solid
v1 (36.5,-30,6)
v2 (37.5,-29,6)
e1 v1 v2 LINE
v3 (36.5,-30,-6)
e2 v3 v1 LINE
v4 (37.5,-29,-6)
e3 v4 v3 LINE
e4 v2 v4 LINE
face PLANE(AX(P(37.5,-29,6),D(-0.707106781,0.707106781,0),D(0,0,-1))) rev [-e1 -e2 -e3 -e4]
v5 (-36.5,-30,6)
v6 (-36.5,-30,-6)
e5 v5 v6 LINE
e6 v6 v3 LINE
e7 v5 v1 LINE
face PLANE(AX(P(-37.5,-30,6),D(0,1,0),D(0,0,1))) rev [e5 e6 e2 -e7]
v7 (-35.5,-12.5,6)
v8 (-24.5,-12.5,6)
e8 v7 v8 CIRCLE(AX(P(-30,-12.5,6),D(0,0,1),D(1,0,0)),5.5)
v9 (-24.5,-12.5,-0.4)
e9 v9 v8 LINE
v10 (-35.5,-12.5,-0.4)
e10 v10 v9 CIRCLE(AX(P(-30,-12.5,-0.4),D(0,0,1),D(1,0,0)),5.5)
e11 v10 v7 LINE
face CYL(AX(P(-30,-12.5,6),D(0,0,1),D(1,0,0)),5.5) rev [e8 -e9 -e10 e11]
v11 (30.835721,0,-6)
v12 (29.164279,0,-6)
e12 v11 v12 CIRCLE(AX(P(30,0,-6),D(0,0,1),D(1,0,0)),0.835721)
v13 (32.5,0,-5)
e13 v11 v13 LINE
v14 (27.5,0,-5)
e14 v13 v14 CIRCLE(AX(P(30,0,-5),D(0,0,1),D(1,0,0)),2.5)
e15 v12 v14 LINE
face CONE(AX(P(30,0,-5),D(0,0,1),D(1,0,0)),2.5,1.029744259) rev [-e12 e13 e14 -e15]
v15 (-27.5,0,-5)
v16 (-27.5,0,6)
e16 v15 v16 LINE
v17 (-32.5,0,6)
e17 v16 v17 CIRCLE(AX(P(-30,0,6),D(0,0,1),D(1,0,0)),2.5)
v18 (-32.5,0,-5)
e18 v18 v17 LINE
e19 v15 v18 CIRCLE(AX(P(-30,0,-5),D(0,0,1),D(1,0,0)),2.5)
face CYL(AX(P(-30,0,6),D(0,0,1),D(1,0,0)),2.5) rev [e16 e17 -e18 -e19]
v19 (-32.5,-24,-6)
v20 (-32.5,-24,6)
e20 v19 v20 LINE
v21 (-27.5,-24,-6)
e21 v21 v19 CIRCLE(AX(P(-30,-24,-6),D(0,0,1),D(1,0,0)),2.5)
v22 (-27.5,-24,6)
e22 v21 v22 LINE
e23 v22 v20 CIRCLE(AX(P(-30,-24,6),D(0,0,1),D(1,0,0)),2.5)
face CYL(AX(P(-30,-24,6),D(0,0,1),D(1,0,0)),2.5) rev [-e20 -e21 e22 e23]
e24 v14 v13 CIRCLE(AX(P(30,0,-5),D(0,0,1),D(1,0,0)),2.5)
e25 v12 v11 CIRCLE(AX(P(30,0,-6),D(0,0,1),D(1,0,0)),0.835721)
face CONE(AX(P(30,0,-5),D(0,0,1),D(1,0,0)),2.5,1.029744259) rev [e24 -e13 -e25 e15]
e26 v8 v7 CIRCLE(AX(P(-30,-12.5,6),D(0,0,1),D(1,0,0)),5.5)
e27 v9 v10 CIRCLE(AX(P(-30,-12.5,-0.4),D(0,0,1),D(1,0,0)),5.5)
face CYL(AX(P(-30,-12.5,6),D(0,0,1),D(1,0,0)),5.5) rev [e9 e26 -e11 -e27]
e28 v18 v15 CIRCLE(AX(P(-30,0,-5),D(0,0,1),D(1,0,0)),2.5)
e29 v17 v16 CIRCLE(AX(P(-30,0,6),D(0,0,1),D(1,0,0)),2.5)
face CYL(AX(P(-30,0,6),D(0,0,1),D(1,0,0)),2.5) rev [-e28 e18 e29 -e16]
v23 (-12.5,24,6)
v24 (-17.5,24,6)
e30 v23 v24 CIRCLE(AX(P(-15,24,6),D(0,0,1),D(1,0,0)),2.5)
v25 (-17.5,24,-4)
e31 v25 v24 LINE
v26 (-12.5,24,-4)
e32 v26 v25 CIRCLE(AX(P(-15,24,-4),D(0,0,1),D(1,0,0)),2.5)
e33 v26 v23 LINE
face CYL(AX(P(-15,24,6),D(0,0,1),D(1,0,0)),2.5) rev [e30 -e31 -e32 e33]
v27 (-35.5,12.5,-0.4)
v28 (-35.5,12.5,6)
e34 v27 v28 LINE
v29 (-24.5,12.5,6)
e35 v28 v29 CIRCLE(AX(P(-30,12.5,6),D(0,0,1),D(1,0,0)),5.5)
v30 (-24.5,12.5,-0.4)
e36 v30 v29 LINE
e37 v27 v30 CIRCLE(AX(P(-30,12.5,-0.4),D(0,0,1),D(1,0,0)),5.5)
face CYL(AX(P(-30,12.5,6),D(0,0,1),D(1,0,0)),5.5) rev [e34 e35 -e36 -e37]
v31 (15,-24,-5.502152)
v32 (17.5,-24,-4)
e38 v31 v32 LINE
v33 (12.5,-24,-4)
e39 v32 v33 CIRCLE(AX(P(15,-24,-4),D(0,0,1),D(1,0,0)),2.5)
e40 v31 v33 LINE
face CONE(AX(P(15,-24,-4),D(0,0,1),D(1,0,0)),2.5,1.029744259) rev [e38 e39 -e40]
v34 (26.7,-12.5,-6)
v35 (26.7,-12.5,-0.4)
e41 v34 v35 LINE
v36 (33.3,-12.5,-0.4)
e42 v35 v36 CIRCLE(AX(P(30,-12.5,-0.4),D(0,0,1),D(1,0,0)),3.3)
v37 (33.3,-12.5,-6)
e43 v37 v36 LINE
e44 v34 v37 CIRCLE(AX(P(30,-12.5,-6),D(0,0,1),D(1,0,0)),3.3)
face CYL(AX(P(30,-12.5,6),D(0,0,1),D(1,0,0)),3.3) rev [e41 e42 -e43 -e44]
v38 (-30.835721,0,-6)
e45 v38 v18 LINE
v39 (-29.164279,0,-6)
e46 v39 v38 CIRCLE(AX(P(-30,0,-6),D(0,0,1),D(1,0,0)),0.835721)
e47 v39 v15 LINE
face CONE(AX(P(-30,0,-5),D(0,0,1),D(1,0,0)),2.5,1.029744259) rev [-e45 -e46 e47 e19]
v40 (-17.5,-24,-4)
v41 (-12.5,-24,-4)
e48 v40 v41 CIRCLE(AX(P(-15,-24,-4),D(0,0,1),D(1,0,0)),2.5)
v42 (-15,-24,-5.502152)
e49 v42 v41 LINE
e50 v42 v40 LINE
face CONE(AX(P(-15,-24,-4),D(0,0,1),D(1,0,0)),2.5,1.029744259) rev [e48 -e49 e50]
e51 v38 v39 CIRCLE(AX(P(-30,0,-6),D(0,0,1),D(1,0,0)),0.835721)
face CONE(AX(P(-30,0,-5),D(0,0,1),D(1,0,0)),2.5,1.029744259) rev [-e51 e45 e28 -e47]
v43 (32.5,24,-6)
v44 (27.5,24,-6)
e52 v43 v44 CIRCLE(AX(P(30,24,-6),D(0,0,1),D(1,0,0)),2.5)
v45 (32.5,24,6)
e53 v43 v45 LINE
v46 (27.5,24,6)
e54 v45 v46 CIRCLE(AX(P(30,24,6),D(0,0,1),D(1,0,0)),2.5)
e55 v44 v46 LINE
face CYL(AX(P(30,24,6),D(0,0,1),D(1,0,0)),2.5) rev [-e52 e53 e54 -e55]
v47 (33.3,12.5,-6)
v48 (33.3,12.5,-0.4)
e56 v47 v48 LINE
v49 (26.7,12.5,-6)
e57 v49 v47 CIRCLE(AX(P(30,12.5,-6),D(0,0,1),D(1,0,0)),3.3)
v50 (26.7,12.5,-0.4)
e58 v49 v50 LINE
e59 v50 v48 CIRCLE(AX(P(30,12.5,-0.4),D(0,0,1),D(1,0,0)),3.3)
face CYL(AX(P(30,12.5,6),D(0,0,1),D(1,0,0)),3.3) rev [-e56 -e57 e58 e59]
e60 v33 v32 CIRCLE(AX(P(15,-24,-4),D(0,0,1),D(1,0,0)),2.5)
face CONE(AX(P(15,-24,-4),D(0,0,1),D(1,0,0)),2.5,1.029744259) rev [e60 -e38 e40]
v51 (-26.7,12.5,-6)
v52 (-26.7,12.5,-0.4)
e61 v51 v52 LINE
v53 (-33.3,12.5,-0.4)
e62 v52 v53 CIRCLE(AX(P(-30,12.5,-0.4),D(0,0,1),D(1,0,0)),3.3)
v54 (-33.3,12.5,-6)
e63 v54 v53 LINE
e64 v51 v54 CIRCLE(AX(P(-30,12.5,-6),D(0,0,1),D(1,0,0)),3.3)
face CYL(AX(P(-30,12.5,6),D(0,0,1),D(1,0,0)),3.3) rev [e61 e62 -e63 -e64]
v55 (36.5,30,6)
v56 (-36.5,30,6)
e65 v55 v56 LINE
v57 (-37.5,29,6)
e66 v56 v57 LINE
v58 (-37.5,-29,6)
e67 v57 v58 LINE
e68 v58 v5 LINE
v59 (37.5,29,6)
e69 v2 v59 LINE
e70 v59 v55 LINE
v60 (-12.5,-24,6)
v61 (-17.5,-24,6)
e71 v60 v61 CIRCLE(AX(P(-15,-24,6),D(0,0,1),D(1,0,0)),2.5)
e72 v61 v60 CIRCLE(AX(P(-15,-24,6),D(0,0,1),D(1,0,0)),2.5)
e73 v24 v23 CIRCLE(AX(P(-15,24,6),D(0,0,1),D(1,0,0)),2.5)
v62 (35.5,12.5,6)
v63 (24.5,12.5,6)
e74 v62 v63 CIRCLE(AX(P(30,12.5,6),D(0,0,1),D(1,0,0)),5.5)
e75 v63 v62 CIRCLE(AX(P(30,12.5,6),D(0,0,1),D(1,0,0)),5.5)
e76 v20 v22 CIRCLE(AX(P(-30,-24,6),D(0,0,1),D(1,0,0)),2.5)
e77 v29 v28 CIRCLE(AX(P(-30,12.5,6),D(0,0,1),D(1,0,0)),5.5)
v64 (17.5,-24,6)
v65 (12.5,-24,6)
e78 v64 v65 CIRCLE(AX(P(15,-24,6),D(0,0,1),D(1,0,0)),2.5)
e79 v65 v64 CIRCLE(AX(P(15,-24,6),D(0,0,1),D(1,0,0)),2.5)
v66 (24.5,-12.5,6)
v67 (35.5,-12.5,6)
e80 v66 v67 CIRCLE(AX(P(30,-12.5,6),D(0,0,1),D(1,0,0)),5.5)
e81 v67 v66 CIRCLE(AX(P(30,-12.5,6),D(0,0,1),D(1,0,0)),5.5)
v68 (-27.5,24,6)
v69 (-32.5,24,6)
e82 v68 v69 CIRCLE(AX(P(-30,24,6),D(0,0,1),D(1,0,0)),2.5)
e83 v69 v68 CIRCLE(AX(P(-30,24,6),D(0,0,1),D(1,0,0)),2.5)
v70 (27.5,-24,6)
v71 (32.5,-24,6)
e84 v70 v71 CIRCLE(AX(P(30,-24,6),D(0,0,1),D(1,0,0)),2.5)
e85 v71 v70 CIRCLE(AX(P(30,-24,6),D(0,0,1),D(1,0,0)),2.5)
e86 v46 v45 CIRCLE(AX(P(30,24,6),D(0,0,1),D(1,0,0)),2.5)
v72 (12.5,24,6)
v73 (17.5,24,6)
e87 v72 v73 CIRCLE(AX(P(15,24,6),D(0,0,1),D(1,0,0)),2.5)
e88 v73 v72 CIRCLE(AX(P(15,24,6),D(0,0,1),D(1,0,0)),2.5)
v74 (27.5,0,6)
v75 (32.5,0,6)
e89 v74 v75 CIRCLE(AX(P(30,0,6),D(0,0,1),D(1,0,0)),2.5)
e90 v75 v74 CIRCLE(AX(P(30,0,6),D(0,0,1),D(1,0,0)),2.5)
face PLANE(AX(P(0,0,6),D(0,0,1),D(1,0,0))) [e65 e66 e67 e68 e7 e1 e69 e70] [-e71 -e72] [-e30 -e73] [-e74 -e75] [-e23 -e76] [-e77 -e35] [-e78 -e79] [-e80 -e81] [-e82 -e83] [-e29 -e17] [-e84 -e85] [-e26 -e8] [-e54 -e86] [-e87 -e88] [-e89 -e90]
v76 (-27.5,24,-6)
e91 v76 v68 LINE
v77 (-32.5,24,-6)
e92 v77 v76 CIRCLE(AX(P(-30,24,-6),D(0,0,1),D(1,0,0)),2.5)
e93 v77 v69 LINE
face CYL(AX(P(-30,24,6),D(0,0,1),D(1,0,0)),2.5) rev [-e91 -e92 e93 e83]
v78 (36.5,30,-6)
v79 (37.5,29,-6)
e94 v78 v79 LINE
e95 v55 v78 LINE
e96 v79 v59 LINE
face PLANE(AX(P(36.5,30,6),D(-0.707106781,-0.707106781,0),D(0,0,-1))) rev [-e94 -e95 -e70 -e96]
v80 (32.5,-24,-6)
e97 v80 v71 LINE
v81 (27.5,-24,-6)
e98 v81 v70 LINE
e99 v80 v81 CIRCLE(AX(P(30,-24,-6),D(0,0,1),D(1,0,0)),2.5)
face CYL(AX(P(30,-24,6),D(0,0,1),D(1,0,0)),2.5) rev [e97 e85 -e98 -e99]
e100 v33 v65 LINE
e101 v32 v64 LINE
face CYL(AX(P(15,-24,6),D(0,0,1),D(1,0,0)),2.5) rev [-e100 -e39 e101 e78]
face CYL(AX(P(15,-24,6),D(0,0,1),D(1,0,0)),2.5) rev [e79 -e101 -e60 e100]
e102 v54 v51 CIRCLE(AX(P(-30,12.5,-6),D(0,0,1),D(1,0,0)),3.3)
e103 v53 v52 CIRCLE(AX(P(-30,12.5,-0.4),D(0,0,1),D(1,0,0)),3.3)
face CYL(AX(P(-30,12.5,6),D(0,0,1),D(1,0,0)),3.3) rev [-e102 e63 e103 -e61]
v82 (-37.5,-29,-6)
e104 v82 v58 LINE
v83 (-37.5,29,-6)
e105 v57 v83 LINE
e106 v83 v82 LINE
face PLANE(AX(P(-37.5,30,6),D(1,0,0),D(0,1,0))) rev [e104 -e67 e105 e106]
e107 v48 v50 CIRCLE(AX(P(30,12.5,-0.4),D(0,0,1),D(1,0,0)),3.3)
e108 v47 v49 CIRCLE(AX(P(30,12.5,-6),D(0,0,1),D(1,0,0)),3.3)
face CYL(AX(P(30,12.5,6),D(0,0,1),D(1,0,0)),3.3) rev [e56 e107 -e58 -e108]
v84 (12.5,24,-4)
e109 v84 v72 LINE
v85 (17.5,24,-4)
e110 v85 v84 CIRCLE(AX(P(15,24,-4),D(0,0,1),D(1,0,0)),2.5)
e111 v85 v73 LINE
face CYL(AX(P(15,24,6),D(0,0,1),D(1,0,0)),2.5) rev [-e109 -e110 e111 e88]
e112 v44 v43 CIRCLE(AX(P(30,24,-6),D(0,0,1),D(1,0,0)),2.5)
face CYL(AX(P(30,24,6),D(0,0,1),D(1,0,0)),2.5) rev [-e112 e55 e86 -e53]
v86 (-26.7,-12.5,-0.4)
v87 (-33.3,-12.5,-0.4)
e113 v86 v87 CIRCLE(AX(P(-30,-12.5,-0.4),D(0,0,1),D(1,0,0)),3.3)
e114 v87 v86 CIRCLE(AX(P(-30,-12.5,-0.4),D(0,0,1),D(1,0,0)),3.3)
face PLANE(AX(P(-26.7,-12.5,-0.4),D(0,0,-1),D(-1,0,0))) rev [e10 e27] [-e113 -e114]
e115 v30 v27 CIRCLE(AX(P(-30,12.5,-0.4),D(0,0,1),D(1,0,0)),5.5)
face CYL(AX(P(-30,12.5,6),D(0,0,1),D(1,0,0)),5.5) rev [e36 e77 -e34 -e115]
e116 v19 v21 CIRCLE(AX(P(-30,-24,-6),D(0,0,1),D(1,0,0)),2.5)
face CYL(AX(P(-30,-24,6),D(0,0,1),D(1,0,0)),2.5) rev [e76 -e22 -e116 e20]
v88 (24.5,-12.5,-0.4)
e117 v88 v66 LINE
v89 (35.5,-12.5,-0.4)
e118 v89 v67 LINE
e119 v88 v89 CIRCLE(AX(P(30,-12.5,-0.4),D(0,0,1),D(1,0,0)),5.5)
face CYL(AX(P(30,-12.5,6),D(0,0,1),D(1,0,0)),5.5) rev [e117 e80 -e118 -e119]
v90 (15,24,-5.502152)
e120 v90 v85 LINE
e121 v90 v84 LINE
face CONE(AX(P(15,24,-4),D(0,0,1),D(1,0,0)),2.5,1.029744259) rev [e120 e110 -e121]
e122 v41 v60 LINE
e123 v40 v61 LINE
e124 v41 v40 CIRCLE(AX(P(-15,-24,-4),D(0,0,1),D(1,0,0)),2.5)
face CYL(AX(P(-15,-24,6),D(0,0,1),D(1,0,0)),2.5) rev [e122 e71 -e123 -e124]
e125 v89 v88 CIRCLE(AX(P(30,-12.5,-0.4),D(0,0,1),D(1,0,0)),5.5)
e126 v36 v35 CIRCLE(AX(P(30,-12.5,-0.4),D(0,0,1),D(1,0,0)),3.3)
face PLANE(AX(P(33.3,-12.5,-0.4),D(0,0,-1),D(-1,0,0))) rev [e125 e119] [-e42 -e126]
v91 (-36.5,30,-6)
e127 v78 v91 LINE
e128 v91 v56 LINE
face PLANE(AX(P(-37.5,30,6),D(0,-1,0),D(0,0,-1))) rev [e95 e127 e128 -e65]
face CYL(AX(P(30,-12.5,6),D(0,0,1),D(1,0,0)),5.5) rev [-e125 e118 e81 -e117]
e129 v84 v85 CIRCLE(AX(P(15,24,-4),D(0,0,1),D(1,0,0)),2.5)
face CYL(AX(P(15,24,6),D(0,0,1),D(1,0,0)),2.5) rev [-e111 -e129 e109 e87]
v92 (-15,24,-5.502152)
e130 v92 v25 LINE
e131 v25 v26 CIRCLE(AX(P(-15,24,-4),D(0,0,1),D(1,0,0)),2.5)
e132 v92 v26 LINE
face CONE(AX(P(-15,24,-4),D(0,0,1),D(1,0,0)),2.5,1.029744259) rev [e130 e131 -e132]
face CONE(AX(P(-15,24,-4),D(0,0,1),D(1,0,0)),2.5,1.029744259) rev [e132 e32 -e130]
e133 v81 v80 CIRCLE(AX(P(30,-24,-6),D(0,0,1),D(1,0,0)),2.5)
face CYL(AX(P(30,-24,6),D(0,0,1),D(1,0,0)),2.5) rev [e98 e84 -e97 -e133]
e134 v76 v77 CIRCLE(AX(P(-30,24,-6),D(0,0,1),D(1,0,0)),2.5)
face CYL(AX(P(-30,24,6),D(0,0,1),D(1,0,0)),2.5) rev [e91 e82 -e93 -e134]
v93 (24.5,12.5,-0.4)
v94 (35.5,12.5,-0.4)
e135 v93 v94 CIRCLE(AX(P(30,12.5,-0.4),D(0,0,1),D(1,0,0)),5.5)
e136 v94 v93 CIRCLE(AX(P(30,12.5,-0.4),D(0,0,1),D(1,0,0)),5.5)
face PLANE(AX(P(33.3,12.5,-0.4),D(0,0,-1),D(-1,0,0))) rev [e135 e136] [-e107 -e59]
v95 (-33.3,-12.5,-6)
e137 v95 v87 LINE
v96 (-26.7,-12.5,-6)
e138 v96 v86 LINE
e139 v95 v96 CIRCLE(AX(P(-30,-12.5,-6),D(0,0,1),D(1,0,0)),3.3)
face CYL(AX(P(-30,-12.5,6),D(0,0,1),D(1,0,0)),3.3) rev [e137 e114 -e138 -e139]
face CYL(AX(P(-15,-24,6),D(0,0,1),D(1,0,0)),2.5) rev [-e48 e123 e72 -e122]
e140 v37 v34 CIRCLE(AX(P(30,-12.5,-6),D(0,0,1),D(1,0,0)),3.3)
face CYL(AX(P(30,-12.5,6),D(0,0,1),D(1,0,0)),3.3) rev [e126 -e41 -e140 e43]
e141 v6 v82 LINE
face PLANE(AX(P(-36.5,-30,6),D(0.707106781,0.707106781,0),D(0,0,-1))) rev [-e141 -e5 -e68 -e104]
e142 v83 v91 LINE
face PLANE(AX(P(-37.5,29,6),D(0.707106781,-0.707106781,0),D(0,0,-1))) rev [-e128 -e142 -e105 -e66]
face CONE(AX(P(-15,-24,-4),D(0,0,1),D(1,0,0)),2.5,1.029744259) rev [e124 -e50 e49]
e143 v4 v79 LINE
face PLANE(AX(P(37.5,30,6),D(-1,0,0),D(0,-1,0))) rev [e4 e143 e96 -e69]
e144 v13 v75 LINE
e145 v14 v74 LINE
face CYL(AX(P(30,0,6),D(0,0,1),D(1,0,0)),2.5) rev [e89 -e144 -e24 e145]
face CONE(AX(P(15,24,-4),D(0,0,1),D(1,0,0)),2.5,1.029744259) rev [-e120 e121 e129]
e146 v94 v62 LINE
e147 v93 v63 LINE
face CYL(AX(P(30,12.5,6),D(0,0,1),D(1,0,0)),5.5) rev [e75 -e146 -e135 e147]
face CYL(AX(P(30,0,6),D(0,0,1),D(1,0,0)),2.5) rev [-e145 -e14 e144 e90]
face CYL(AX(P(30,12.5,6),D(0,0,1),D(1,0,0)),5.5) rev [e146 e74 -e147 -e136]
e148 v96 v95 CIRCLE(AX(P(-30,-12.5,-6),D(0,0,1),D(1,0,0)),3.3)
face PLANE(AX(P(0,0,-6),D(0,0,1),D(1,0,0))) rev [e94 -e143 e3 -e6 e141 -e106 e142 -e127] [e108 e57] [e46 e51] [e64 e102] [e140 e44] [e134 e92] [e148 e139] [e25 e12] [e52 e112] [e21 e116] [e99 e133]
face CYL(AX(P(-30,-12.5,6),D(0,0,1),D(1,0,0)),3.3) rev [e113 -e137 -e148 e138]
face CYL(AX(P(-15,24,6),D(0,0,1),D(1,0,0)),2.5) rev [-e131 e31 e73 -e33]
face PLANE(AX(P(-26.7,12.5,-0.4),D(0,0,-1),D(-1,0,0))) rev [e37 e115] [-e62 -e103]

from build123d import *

# Parameters (mm, degrees)
SKETCH1_W                                           = 75
SKETCH1_H                                           = 60
BOSS_EXTRUDE1_DEPTH                                 = 6
M6_TAPPED_HOLE1_D                                   = 5
CBORE_FOR_M6_HEX_SOCKET_HEAD_CAP_SCREW1_D           = 6.6
CBORE_FOR_M6_HEX_SOCKET_HEAD_CAP_SCREW1_CBORE_D     = 11
CBORE_FOR_M6_HEX_SOCKET_HEAD_CAP_SCREW1_CBORE_DEPTH = 6.4
BLIND_PIN_HOLE3_SIZE_MM_D                           = 5
BLIND_PIN_HOLE3_SIZE_MM_DEPTH                       = 11
BLIND_PIN_HOLE3_SIZE_MM_TIP                         = 1.502151548
MM_3_D                                              = 5
MM_3_DEPTH                                          = 10
MM_3_TIP                                            = 1.502151548
CHAMFER1_SIZE                                       = 1


with BuildPart() as part:
    # Sketch1 → Boss-Extrude1 (new, symmetric)
    with BuildSketch(Plane.XY):
        Rectangle(SKETCH1_W, SKETCH1_H)
    extrude(amount=BOSS_EXTRUDE1_DEPTH, both=True)

    # M6 Tapped Hole1 (through all)
    with Locations(Plane.XY.offset(6)):
        with Locations((30, 24), (30, -24), (-30, -24), (-30, 24)):
            Hole(M6_TAPPED_HOLE1_D / 2)

    # CBORE for M6 Hex Socket Head Cap Screw1 (through all)
    with Locations(Plane.XY.offset(6)):
        with Locations((-30, 12.5), (30, 12.5), (-30, -12.5), (30, -12.5)):
            CounterBoreHole(CBORE_FOR_M6_HEX_SOCKET_HEAD_CAP_SCREW1_D / 2, CBORE_FOR_M6_HEX_SOCKET_HEAD_CAP_SCREW1_CBORE_D / 2, CBORE_FOR_M6_HEX_SOCKET_HEAD_CAP_SCREW1_CBORE_DEPTH)

    # Blind Pin Hole3 (size mm)
    with Locations(Plane.XY.offset(6)):
        with Locations((-30, 0), (30, 0)):
            Hole(BLIND_PIN_HOLE3_SIZE_MM_D / 2, depth=BLIND_PIN_HOLE3_SIZE_MM_DEPTH)
            with Locations((0, 0, -(BLIND_PIN_HOLE3_SIZE_MM_DEPTH + BLIND_PIN_HOLE3_SIZE_MM_TIP / 2))):  # 118° drill point
                Cone(0, BLIND_PIN_HOLE3_SIZE_MM_D / 2, BLIND_PIN_HOLE3_SIZE_MM_TIP, mode=Mode.SUBTRACT)

    # 大小mm 暗销孔3
    with Locations(Plane.XY.offset(6)):
        with Locations((-15, 24), (15, -24), (15, 24), (-15, -24)):
            Hole(MM_3_D / 2, depth=MM_3_DEPTH)
            with Locations((0, 0, -(MM_3_DEPTH + MM_3_TIP / 2))):  # 118° drill point
                Cone(0, MM_3_D / 2, MM_3_TIP, mode=Mode.SUBTRACT)

    # Chamfer1
    chamfer1_edges = [part.edges().sort_by_distance(p)[0] for p in [
        (37.5, -30, 0),
        (-37.5, -30, 0),
        (-37.5, 30, 0),
        (37.5, 30, 0),
    ]]
    chamfer(chamfer1_edges, length=CHAMFER1_SIZE)


solid = part.part
